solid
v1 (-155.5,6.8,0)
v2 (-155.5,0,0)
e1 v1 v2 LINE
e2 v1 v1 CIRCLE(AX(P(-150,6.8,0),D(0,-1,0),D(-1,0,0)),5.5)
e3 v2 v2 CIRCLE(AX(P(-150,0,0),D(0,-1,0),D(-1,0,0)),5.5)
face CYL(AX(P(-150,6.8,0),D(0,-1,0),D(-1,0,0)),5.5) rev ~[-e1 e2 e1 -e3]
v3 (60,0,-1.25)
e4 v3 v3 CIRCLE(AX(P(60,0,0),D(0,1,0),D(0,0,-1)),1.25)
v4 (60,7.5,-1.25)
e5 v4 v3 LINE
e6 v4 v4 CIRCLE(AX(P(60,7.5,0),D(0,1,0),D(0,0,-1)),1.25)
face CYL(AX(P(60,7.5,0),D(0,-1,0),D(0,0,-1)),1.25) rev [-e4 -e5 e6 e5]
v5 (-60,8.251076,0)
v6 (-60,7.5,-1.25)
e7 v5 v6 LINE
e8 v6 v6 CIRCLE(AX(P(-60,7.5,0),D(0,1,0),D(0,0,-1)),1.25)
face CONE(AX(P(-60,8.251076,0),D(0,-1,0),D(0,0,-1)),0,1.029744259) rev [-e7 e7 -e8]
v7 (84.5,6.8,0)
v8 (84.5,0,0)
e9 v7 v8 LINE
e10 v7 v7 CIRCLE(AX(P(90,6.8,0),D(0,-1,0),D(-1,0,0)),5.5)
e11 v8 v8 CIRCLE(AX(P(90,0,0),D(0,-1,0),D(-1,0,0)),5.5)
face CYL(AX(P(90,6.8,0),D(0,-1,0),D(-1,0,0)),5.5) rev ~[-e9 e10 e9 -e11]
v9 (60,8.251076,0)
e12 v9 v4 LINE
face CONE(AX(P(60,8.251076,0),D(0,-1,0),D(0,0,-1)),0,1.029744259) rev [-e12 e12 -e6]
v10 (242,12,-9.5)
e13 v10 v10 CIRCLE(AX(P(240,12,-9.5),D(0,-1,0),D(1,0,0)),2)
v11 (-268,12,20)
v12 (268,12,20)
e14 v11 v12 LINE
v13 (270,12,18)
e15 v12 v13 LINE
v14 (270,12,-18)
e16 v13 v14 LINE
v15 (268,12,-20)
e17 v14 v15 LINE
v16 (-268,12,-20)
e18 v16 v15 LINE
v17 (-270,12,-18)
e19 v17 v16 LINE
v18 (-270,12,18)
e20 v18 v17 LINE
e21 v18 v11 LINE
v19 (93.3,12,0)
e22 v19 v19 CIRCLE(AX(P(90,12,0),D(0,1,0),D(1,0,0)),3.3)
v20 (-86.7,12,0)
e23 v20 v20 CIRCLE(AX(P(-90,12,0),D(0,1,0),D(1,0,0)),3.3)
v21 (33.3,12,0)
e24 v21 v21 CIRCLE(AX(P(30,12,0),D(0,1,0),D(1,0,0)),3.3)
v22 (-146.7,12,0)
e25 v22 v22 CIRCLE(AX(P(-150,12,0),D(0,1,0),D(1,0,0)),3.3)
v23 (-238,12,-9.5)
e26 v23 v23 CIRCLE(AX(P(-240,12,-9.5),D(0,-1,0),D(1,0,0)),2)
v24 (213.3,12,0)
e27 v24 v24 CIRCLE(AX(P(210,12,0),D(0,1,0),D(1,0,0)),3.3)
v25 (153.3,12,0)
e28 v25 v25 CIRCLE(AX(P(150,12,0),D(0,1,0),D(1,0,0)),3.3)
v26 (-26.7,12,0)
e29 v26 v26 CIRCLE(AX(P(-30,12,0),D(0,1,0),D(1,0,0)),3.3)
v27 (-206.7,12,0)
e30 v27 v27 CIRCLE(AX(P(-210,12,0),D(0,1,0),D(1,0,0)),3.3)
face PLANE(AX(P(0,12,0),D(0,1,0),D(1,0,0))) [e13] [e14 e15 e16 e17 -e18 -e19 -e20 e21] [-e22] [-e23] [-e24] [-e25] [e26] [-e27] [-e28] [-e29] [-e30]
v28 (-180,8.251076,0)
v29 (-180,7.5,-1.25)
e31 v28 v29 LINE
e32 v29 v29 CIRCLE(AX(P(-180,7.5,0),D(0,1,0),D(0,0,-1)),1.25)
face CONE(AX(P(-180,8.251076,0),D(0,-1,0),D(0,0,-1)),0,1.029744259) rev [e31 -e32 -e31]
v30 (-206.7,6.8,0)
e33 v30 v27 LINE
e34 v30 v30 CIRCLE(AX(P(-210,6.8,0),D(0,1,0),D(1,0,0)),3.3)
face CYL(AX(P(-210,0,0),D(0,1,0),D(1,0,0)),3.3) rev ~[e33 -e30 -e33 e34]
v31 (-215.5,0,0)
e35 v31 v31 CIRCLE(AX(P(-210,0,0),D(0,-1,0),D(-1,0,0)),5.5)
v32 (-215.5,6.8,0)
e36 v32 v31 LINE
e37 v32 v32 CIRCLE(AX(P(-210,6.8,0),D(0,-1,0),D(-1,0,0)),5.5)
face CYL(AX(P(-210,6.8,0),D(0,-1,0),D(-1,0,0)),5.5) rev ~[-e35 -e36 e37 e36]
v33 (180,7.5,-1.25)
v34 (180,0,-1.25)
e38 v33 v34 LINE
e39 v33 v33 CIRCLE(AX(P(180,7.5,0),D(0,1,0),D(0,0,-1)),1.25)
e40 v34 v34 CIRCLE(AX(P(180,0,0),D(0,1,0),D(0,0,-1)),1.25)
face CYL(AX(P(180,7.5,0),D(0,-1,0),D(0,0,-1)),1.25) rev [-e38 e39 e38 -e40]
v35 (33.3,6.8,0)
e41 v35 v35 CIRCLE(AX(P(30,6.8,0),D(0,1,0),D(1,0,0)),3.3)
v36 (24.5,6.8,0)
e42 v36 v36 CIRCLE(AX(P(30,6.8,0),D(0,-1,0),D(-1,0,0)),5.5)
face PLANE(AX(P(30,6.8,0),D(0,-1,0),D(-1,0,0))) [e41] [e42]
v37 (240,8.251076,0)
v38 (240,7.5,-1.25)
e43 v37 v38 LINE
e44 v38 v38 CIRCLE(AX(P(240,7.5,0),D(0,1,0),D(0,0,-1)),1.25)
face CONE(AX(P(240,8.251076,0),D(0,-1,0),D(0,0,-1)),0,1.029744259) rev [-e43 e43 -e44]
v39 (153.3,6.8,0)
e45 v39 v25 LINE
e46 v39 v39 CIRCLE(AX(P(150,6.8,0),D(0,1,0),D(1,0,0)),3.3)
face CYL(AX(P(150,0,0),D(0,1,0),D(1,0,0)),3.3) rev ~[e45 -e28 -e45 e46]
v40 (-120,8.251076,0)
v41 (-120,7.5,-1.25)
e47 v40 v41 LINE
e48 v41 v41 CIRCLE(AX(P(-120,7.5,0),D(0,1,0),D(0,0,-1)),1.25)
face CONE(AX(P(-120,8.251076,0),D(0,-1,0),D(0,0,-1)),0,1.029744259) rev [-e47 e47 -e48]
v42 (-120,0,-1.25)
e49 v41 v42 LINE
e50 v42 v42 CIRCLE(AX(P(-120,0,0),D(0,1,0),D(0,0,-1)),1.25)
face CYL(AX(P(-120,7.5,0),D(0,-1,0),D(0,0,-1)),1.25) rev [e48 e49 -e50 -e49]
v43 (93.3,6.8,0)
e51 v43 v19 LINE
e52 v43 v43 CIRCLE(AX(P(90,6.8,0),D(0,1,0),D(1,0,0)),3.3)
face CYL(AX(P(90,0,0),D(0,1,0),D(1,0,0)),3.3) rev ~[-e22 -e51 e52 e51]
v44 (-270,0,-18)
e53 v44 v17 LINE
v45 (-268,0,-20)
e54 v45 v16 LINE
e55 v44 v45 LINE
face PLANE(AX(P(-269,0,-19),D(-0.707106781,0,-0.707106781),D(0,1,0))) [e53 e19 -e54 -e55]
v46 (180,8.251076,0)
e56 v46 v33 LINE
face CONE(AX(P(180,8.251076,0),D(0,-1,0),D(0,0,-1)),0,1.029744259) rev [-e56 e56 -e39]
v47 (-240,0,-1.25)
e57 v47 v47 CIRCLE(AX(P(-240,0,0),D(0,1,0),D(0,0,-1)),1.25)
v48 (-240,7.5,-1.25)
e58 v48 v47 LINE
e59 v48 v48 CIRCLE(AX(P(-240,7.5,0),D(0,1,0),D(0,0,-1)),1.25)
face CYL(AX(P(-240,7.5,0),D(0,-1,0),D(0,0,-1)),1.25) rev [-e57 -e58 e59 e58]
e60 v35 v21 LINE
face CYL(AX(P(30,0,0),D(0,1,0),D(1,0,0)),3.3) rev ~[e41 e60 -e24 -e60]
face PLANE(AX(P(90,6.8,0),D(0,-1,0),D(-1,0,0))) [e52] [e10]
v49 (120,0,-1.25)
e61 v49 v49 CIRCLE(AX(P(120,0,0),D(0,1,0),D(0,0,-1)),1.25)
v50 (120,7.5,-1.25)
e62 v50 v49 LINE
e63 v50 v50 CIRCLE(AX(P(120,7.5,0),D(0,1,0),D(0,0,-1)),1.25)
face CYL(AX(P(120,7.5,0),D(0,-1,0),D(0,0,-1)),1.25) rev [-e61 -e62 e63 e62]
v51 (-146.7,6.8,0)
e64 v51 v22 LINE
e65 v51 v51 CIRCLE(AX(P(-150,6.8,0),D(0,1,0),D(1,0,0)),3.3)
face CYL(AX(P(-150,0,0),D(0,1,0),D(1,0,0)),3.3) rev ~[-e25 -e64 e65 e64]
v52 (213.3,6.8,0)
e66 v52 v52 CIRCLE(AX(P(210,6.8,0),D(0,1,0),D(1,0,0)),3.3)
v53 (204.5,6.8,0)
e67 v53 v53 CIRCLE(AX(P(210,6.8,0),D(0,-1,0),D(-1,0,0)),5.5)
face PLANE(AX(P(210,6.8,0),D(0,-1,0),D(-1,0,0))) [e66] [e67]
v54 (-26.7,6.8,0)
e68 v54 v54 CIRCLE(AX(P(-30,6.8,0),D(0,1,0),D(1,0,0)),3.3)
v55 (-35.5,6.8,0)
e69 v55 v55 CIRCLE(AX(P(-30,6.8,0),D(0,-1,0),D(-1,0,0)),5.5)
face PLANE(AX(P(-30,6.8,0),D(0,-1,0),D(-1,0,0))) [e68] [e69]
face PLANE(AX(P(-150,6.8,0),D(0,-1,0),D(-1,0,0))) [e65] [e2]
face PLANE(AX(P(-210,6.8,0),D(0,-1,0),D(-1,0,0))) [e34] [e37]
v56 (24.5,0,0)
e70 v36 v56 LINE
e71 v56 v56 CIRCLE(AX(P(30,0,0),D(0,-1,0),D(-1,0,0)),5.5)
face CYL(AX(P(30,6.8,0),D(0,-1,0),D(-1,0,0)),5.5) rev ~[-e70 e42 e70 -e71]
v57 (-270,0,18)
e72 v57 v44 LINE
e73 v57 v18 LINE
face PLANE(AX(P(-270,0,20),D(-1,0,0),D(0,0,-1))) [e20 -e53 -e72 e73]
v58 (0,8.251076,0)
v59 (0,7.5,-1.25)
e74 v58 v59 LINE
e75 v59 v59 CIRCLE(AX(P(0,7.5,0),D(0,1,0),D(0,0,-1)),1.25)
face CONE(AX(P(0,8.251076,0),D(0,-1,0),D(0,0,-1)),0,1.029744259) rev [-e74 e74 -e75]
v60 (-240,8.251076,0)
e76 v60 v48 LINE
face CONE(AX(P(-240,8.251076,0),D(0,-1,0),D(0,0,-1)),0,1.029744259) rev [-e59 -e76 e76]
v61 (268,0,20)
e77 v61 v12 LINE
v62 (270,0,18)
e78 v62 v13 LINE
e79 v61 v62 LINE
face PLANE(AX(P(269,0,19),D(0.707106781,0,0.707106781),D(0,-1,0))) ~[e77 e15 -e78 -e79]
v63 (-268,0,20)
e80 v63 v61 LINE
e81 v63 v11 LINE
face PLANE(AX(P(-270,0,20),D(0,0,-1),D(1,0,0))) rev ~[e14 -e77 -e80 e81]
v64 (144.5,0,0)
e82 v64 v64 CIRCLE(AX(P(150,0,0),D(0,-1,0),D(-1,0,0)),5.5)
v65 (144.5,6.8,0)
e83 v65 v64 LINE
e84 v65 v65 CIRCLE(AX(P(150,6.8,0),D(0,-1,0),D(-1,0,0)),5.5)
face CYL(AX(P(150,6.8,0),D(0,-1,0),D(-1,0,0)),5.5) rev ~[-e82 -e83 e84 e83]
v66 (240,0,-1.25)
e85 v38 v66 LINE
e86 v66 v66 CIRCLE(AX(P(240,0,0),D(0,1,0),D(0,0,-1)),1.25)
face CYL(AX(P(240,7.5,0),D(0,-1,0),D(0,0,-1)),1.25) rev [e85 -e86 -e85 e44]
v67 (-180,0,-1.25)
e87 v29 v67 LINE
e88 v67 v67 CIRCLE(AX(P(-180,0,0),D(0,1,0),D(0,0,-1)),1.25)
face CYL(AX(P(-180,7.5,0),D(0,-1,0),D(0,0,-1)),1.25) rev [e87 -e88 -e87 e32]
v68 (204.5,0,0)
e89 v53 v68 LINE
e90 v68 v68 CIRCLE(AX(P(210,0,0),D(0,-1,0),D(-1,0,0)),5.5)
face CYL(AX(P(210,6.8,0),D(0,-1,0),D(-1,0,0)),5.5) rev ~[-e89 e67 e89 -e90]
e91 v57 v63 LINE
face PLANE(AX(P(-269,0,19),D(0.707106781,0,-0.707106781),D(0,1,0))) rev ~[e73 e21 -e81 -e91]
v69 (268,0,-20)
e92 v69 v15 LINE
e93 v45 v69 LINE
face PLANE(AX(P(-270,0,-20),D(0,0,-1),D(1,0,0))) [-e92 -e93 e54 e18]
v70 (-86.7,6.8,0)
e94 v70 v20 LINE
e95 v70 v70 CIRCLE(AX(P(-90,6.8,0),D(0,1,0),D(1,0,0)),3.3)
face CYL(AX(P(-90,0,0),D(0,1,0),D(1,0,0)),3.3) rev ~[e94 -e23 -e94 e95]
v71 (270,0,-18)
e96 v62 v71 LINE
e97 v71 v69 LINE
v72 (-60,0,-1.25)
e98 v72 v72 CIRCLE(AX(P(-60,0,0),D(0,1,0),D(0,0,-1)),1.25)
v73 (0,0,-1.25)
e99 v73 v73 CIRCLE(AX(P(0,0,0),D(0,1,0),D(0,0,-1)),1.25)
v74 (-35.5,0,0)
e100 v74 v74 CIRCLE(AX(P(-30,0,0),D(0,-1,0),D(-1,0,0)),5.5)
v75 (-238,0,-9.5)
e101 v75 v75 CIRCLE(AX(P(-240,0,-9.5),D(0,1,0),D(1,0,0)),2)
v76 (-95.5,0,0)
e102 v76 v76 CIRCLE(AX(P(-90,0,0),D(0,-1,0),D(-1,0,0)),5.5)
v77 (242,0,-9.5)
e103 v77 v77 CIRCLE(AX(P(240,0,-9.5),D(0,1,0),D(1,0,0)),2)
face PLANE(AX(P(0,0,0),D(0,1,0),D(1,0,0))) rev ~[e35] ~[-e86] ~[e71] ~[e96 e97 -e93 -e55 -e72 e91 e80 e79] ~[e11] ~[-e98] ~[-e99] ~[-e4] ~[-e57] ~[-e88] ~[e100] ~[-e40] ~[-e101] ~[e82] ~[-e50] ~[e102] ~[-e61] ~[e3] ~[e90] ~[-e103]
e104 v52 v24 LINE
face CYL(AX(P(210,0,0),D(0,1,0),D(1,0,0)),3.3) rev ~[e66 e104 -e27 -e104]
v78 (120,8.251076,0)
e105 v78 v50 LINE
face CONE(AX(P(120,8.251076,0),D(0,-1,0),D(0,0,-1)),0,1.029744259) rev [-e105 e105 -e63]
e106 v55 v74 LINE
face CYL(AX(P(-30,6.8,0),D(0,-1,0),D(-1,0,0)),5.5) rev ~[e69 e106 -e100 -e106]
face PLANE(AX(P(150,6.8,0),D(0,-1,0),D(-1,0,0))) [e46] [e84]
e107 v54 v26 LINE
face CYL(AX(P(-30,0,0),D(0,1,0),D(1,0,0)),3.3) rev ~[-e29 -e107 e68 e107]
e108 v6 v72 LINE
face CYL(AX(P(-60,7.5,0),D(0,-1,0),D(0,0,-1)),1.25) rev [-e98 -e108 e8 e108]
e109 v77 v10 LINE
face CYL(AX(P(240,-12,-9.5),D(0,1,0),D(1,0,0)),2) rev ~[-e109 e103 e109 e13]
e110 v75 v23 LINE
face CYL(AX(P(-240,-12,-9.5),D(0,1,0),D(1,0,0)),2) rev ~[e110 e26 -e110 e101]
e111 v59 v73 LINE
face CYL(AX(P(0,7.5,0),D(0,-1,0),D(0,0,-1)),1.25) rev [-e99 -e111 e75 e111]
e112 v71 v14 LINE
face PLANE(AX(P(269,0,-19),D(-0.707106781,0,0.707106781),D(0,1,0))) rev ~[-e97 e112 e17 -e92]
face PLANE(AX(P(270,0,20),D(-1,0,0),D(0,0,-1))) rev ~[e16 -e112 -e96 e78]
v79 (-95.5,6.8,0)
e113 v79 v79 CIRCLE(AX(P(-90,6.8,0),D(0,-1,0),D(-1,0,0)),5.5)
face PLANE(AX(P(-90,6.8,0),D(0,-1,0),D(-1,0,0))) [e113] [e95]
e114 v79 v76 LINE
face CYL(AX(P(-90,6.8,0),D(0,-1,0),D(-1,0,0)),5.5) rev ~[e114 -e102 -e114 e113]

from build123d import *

# Parameters (mm, degrees)
SKETCH_1_W                   = 540
SKETCH_1_H                   = 40
EXTRUDE_1_DEPTH              = 12
CHAMFER_1_SIZE               = 2
F_4_0MM_1_D                  = 4
F_4_0MM_1_DEPTH              = 12
F_4_0MM_1_TIP                = 1.201721238
PATTERN_LINEAR_4_COUNT       = 9
PATTERN_LINEAR_4_PITCH       = 60
HOLE_WIZARD_M6_1_D           = 6.6
HOLE_WIZARD_M6_1_CBORE_D     = 11
HOLE_WIZARD_M6_1_CBORE_DEPTH = 6.8
PATTERN_LINEAR_5_COUNT       = 8
PATTERN_LINEAR_5_PITCH       = 60


with BuildPart() as part:
    # 草图1 → 凸台-拉伸1 (new body)
    with BuildSketch(Plane(origin=(0, 0, 0), x_dir=(1, 0, 0), z_dir=(0, 1, 0))):
        Rectangle(SKETCH_1_W, SKETCH_1_H)
    extrude(amount=EXTRUDE_1_DEPTH)

    # 倒角1
    chamfer_1_edges = [part.edges().sort_by_distance(p)[0] for p in [
        (270, 6, 20),
        (-270, 6, 20),
        (-270, 6, -20),
        (270, 6, -20),
    ]]
    chamfer(chamfer_1_edges, length=CHAMFER_1_SIZE)

    # Ø4.0mm 暗销孔1
    with Locations(Plane(origin=(0, 0, 0), x_dir=(-1, 0, 0), z_dir=(0, -1, 0))):
        with Locations((-240, 9.5), (240, 9.5)):
            Hole(F_4_0MM_1_D / 2, depth=F_4_0MM_1_DEPTH)
            with Locations((0, 0, -(F_4_0MM_1_DEPTH + F_4_0MM_1_TIP / 2))):  # 118° drill point
                Cone(0, F_4_0MM_1_D / 2, F_4_0MM_1_TIP, mode=Mode.SUBTRACT)

    # 草图6 → M3 螺纹孔1 (revolve, cut)
    with BuildSketch(Plane(origin=(240, 0, 0), x_dir=(0, 0, -1), z_dir=(1, 0, 0))):
        Polygon((0, 0), (0, 8.251075774), (1.25, 7.5), (1.25, 0), align=None)
    hole_wizard_m3_1 = revolve(axis=Axis((240, -6.35, 0), (0, 1, 0)), mode=Mode.SUBTRACT)

    # 阵列(线性)4: M3 螺纹孔1 ×9
    with Locations(*[(-i * PATTERN_LINEAR_4_PITCH, 0, 0) for i in range(1, PATTERN_LINEAR_4_COUNT)]):
        add(hole_wizard_m3_1, mode=Mode.SUBTRACT)

    # M6 六角圆柱头螺钉的柱形沉头孔1 (through all)
    with Locations(Plane(origin=(0, 0, 0), x_dir=(-1, 0, 0), z_dir=(0, -1, 0))):
        with Locations((210, 0)):
            hole_wizard_m6_1 = CounterBoreHole(HOLE_WIZARD_M6_1_D / 2, HOLE_WIZARD_M6_1_CBORE_D / 2, HOLE_WIZARD_M6_1_CBORE_DEPTH)

    # 阵列(线性)5: M6 六角圆柱头螺钉的柱形沉头孔1 ×8
    with Locations(*[(i * PATTERN_LINEAR_5_PITCH, 0, 0) for i in range(1, PATTERN_LINEAR_5_COUNT)]):
        add(hole_wizard_m6_1, mode=Mode.SUBTRACT)


solid = part.part
